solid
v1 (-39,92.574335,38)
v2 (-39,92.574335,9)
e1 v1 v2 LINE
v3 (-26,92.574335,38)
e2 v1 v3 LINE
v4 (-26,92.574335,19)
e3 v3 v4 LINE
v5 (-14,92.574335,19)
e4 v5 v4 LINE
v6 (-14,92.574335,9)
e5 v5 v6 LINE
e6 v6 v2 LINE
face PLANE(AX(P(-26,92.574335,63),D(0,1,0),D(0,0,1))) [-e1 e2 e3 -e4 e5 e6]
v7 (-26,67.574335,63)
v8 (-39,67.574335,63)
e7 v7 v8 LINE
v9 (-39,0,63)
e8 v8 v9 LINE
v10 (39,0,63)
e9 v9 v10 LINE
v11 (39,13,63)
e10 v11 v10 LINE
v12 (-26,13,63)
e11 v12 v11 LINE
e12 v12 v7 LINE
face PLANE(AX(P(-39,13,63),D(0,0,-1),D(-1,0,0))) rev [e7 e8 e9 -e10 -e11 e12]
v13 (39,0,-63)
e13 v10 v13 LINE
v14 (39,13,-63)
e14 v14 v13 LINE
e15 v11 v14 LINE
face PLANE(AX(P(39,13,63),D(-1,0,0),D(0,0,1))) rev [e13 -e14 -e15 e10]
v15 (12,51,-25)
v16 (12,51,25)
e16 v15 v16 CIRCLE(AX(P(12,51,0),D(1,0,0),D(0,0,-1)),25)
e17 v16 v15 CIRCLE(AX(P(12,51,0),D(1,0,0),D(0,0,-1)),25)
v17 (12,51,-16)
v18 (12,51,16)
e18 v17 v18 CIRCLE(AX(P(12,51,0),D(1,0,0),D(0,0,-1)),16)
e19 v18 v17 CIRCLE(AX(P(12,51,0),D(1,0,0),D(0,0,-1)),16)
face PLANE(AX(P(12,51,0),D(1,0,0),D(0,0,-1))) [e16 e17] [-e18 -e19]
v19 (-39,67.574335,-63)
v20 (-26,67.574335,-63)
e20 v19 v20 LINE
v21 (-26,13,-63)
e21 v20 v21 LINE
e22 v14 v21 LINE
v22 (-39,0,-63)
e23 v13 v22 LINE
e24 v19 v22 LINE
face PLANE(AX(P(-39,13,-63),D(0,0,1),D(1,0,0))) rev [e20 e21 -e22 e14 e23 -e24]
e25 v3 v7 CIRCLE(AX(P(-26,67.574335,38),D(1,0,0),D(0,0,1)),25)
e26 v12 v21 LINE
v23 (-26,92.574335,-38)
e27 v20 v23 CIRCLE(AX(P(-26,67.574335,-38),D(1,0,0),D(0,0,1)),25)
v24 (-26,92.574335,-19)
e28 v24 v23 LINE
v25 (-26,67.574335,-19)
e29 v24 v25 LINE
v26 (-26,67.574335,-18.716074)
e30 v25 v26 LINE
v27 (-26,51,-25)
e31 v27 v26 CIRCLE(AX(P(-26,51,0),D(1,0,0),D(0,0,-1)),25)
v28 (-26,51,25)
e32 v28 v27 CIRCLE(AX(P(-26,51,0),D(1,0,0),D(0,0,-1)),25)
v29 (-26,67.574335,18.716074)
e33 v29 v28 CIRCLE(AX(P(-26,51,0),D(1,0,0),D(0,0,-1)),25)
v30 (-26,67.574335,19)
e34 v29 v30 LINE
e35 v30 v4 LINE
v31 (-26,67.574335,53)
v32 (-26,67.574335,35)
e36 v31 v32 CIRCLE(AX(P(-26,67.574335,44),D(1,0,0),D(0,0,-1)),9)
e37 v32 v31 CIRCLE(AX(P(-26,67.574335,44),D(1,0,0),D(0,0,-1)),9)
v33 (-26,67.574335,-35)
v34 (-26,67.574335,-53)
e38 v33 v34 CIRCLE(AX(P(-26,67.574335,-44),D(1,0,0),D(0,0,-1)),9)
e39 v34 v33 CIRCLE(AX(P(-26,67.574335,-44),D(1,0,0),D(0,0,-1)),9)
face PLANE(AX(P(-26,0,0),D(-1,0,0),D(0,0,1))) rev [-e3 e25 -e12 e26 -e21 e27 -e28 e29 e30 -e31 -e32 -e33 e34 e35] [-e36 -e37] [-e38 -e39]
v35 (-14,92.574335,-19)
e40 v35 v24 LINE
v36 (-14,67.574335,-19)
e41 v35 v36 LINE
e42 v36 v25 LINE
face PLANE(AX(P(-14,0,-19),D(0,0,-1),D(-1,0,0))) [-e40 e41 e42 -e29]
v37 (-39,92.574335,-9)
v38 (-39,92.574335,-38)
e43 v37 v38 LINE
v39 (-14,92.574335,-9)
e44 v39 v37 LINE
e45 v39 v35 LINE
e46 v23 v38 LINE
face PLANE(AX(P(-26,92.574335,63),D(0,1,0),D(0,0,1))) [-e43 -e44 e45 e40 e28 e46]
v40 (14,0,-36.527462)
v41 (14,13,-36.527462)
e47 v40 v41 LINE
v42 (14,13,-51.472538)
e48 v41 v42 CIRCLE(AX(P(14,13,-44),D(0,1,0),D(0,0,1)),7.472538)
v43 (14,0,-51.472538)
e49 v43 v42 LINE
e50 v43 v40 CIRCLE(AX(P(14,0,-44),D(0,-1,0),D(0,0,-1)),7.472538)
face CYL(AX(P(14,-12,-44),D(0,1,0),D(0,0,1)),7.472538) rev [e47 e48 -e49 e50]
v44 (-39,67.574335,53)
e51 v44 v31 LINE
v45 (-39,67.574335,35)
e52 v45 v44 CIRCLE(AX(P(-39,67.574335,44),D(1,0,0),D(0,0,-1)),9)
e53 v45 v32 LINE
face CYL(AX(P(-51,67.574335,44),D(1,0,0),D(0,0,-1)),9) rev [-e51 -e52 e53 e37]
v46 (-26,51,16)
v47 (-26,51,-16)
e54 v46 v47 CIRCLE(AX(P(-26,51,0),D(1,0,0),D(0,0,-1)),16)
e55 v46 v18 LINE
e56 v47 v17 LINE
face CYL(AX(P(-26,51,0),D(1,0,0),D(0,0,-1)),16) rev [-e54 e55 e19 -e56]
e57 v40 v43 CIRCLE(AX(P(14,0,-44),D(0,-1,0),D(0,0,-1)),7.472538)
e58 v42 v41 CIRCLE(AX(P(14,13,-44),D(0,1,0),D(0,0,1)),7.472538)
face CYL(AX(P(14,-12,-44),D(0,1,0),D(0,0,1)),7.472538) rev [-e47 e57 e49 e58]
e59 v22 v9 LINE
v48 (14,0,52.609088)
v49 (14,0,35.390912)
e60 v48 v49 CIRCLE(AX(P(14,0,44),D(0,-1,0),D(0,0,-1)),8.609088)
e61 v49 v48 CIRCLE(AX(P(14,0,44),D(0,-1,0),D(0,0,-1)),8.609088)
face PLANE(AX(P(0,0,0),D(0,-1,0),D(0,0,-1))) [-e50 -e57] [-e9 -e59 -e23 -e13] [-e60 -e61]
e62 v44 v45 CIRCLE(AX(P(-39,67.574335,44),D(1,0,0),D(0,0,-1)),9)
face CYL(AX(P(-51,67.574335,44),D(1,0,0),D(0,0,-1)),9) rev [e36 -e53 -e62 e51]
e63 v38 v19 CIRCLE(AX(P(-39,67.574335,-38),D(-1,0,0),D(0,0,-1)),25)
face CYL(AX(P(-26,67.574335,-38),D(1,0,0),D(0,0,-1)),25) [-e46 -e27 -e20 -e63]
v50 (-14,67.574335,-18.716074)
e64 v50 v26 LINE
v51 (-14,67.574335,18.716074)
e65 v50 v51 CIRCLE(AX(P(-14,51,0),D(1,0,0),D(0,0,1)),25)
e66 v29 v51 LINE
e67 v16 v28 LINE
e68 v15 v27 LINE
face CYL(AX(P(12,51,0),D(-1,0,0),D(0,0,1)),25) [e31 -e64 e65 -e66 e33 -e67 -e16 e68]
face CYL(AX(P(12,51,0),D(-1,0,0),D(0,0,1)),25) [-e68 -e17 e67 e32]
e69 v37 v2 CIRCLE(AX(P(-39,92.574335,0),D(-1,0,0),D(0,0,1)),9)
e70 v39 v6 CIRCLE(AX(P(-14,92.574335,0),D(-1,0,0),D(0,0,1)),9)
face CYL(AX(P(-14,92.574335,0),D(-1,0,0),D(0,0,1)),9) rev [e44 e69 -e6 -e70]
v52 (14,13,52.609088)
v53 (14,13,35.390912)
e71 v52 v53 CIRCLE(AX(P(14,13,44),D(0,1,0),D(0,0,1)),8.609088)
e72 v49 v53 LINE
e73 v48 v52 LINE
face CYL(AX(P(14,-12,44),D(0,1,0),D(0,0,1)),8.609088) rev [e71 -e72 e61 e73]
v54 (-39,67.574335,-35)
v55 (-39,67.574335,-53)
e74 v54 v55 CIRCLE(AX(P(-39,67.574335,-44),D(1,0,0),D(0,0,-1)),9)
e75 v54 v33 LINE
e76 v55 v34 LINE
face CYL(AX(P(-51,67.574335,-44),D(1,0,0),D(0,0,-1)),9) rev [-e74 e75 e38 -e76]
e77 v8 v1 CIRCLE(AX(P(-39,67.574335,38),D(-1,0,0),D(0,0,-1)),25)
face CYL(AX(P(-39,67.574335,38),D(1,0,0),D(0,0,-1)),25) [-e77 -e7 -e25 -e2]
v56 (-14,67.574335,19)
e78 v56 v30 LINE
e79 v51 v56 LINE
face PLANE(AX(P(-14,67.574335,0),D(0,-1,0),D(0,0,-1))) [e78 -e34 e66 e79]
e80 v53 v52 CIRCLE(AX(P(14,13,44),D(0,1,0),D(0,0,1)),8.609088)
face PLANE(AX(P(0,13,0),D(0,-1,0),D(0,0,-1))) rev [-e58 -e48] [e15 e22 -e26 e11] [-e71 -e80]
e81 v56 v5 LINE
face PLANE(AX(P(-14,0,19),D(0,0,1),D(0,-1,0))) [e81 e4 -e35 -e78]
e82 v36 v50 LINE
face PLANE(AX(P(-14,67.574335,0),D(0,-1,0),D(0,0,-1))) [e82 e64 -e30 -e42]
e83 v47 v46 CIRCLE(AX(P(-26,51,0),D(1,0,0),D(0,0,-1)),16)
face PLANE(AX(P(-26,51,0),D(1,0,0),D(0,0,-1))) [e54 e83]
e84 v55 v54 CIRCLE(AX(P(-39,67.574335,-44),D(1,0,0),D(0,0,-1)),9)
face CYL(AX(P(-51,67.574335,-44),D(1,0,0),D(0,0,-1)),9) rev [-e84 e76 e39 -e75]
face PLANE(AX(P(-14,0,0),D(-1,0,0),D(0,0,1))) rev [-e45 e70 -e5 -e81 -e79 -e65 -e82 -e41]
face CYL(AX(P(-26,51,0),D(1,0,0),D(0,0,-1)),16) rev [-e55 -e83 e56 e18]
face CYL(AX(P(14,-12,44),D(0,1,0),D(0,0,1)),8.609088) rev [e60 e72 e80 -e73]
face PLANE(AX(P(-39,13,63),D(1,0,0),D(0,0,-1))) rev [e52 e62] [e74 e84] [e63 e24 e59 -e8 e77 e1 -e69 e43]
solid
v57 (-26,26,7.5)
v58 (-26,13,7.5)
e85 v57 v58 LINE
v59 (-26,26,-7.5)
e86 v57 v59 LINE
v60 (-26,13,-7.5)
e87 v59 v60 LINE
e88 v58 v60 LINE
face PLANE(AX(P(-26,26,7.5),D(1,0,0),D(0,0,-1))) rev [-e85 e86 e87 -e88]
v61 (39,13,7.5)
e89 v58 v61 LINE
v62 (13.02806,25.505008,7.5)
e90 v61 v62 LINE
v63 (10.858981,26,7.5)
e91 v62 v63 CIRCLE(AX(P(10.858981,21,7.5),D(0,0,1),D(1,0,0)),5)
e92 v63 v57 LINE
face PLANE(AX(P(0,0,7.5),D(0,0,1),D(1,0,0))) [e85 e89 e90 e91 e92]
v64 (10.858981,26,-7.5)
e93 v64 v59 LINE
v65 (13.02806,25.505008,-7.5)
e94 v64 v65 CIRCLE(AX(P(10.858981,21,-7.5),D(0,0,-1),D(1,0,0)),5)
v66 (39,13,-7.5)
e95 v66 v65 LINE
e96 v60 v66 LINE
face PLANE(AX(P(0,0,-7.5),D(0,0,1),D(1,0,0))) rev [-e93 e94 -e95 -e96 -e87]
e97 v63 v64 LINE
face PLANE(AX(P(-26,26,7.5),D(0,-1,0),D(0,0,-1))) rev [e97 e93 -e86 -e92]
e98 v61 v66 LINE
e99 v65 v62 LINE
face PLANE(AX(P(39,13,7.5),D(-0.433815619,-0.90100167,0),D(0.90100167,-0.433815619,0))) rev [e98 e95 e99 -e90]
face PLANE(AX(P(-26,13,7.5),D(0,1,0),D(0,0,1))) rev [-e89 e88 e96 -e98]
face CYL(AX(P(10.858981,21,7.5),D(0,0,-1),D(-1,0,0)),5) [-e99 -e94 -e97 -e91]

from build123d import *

# Parameters (mm, degrees)
BASE_PLATE_SKETCH_W           = 78
BASE_PLATE_SKETCH_H           = 126
BASE_PLATE_126X78X13_DEPTH    = 13
UPRIGHT_PLATE_SKETCH_W        = 126
UPRIGHT_PLATE_SKETCH_H        = 92.574334666
UPRIGHT_PLATE_DEPTH           = 13
UPRIGHT_CORNER_FILLET_R25_A_R = 25
UPRIGHT_CORNER_FILLET_R25_B_R = 25
UPRIGHT_TOP_BLOCK_DEPTH       = 25
TOP_NOTCH_SKETCH_R            = 9
TOP_NOTCH_18_DEPTH            = 25
UPRIGHT_HOLES_SKETCH_R        = 9
UPRIGHT_HOLES_2X_DEPTH        = 25
BASE_HOLES_SKETCH_R           = 7.472538325
BASE_HOLES_SKETCH_R_2         = 8.609088436
BASE_MOUNTING_HOLES_2X_DEPTH  = 25
HUB_BOSS_SKETCH_R             = 25
HUB_BOSS_DEPTH                = 38
HUB_BORE_SKETCH_R             = 16
HUB_BORE_DEPTH                = 38
GUSSET_RIB_DEPTH              = 7.5
GUSSET_RIB_FILLET_R5_R        = 5


with BuildPart() as part:
    # Base Plate Sketch → Base Plate 126x78x13 (new body)
    with BuildSketch(Plane(origin=(0, 0, 0), x_dir=(1, 0, 0), z_dir=(0, 1, 0))):
        Rectangle(BASE_PLATE_SKETCH_W, BASE_PLATE_SKETCH_H)
    extrude(amount=BASE_PLATE_126X78X13_DEPTH)

    # Upright Plate Sketch → Upright Plate (add)
    with BuildSketch(Plane.ZY.offset(39)):
        with Locations((0, 46.287167333)):
            Rectangle(UPRIGHT_PLATE_SKETCH_W, UPRIGHT_PLATE_SKETCH_H)
    extrude(amount=-UPRIGHT_PLATE_DEPTH)

    # Upright Corner Fillet R25 A
    upright_corner_fillet_r25_a_edges = [part.edges().sort_by_distance(p)[0] for p in [
        (-32.5, 92.574334666, 63),
    ]]
    fillet(upright_corner_fillet_r25_a_edges, radius=UPRIGHT_CORNER_FILLET_R25_A_R)

    # Upright Corner Fillet R25 B
    upright_corner_fillet_r25_b_edges = [part.edges().sort_by_distance(p)[0] for p in [
        (-32.5, 92.574334666, -63),
    ]]
    fillet(upright_corner_fillet_r25_b_edges, radius=UPRIGHT_CORNER_FILLET_R25_B_R)

    # Upright Top Block Sketch → Upright Top Block (add)
    with BuildSketch(Plane.ZY.offset(39)):
        with BuildLine():
            ThreePointArc((9, 92.574334666), (0, 83.574334666), (-9, 92.574334666))
            Line((-9, 92.574334666), (-19, 92.574334666))
            Line((-19, 92.574334666), (-19, 67.574334666))
            Line((-19, 67.574334666), (19, 67.574334666))
            Line((19, 67.574334666), (19, 92.574334666))
            Line((19, 92.574334666), (9, 92.574334666))
        make_face()
    extrude(amount=-UPRIGHT_TOP_BLOCK_DEPTH)

    # Top Notch Sketch → Top Notch Ø18 (cut)
    with BuildSketch(Plane.ZY.offset(39)):
        with Locations((0, 92.574334666)):
            Circle(TOP_NOTCH_SKETCH_R)
    extrude(amount=-TOP_NOTCH_18_DEPTH, mode=Mode.SUBTRACT)

    # Upright Holes Sketch → Upright Holes 2x (cut)
    with BuildSketch(Plane(origin=(-26, 0, 0), x_dir=(0, 0, -1), z_dir=(1, 0, 0))):
        with Locations((-44, 67.574334666)):
            Circle(UPRIGHT_HOLES_SKETCH_R)
        with Locations((44, 67.574334666)):
            Circle(UPRIGHT_HOLES_SKETCH_R)
    extrude(amount=-UPRIGHT_HOLES_2X_DEPTH, mode=Mode.SUBTRACT)

    # Base Holes Sketch → Base Mounting Holes 2x (cut)
    with BuildSketch(Plane(origin=(0, 13, 0), x_dir=(1, 0, 0), z_dir=(0, 1, 0))):
        with Locations(Location((14, 44, 0), (0, 0, 270))):
            Circle(BASE_HOLES_SKETCH_R)
        with Locations(Location((14, -44, 0), (0, 0, 270))):
            Circle(BASE_HOLES_SKETCH_R_2)
    extrude(amount=-BASE_MOUNTING_HOLES_2X_DEPTH, mode=Mode.SUBTRACT)

    # Hub Boss Sketch → Hub Boss (add)
    with BuildSketch(Plane(origin=(-26, 0, 0), x_dir=(0, 0, -1), z_dir=(1, 0, 0))):
        with Locations(Location((0, 51, 0), (0, 0, 138.472963652))):
            Circle(HUB_BOSS_SKETCH_R)
    extrude(amount=HUB_BOSS_DEPTH)

    # Hub Bore Sketch → Hub Bore (cut)
    with BuildSketch(Plane(origin=(12, 0, 0), x_dir=(0, 0, -1), z_dir=(1, 0, 0))):
        with Locations((0, 51)):
            Circle(HUB_BORE_SKETCH_R)
    extrude(amount=-HUB_BORE_DEPTH, mode=Mode.SUBTRACT)


with BuildPart() as body_2:
    # Gusset Rib Sketch → Gusset Rib (new, symmetric)
    with BuildSketch(Plane.XY):
        Polygon((-26, 26), (12, 26), (39, 13), (-26, 13), align=None)
    extrude(amount=GUSSET_RIB_DEPTH, both=True)

    # Gusset Rib Fillet R5
    gusset_rib_fillet_r5_edges = [body_2.edges().sort_by_distance(p)[0] for p in [
        (12, 26, 0),
    ]]
    fillet(gusset_rib_fillet_r5_edges, radius=GUSSET_RIB_FILLET_R5_R)


solid = Compound([part.part, body_2.part])
